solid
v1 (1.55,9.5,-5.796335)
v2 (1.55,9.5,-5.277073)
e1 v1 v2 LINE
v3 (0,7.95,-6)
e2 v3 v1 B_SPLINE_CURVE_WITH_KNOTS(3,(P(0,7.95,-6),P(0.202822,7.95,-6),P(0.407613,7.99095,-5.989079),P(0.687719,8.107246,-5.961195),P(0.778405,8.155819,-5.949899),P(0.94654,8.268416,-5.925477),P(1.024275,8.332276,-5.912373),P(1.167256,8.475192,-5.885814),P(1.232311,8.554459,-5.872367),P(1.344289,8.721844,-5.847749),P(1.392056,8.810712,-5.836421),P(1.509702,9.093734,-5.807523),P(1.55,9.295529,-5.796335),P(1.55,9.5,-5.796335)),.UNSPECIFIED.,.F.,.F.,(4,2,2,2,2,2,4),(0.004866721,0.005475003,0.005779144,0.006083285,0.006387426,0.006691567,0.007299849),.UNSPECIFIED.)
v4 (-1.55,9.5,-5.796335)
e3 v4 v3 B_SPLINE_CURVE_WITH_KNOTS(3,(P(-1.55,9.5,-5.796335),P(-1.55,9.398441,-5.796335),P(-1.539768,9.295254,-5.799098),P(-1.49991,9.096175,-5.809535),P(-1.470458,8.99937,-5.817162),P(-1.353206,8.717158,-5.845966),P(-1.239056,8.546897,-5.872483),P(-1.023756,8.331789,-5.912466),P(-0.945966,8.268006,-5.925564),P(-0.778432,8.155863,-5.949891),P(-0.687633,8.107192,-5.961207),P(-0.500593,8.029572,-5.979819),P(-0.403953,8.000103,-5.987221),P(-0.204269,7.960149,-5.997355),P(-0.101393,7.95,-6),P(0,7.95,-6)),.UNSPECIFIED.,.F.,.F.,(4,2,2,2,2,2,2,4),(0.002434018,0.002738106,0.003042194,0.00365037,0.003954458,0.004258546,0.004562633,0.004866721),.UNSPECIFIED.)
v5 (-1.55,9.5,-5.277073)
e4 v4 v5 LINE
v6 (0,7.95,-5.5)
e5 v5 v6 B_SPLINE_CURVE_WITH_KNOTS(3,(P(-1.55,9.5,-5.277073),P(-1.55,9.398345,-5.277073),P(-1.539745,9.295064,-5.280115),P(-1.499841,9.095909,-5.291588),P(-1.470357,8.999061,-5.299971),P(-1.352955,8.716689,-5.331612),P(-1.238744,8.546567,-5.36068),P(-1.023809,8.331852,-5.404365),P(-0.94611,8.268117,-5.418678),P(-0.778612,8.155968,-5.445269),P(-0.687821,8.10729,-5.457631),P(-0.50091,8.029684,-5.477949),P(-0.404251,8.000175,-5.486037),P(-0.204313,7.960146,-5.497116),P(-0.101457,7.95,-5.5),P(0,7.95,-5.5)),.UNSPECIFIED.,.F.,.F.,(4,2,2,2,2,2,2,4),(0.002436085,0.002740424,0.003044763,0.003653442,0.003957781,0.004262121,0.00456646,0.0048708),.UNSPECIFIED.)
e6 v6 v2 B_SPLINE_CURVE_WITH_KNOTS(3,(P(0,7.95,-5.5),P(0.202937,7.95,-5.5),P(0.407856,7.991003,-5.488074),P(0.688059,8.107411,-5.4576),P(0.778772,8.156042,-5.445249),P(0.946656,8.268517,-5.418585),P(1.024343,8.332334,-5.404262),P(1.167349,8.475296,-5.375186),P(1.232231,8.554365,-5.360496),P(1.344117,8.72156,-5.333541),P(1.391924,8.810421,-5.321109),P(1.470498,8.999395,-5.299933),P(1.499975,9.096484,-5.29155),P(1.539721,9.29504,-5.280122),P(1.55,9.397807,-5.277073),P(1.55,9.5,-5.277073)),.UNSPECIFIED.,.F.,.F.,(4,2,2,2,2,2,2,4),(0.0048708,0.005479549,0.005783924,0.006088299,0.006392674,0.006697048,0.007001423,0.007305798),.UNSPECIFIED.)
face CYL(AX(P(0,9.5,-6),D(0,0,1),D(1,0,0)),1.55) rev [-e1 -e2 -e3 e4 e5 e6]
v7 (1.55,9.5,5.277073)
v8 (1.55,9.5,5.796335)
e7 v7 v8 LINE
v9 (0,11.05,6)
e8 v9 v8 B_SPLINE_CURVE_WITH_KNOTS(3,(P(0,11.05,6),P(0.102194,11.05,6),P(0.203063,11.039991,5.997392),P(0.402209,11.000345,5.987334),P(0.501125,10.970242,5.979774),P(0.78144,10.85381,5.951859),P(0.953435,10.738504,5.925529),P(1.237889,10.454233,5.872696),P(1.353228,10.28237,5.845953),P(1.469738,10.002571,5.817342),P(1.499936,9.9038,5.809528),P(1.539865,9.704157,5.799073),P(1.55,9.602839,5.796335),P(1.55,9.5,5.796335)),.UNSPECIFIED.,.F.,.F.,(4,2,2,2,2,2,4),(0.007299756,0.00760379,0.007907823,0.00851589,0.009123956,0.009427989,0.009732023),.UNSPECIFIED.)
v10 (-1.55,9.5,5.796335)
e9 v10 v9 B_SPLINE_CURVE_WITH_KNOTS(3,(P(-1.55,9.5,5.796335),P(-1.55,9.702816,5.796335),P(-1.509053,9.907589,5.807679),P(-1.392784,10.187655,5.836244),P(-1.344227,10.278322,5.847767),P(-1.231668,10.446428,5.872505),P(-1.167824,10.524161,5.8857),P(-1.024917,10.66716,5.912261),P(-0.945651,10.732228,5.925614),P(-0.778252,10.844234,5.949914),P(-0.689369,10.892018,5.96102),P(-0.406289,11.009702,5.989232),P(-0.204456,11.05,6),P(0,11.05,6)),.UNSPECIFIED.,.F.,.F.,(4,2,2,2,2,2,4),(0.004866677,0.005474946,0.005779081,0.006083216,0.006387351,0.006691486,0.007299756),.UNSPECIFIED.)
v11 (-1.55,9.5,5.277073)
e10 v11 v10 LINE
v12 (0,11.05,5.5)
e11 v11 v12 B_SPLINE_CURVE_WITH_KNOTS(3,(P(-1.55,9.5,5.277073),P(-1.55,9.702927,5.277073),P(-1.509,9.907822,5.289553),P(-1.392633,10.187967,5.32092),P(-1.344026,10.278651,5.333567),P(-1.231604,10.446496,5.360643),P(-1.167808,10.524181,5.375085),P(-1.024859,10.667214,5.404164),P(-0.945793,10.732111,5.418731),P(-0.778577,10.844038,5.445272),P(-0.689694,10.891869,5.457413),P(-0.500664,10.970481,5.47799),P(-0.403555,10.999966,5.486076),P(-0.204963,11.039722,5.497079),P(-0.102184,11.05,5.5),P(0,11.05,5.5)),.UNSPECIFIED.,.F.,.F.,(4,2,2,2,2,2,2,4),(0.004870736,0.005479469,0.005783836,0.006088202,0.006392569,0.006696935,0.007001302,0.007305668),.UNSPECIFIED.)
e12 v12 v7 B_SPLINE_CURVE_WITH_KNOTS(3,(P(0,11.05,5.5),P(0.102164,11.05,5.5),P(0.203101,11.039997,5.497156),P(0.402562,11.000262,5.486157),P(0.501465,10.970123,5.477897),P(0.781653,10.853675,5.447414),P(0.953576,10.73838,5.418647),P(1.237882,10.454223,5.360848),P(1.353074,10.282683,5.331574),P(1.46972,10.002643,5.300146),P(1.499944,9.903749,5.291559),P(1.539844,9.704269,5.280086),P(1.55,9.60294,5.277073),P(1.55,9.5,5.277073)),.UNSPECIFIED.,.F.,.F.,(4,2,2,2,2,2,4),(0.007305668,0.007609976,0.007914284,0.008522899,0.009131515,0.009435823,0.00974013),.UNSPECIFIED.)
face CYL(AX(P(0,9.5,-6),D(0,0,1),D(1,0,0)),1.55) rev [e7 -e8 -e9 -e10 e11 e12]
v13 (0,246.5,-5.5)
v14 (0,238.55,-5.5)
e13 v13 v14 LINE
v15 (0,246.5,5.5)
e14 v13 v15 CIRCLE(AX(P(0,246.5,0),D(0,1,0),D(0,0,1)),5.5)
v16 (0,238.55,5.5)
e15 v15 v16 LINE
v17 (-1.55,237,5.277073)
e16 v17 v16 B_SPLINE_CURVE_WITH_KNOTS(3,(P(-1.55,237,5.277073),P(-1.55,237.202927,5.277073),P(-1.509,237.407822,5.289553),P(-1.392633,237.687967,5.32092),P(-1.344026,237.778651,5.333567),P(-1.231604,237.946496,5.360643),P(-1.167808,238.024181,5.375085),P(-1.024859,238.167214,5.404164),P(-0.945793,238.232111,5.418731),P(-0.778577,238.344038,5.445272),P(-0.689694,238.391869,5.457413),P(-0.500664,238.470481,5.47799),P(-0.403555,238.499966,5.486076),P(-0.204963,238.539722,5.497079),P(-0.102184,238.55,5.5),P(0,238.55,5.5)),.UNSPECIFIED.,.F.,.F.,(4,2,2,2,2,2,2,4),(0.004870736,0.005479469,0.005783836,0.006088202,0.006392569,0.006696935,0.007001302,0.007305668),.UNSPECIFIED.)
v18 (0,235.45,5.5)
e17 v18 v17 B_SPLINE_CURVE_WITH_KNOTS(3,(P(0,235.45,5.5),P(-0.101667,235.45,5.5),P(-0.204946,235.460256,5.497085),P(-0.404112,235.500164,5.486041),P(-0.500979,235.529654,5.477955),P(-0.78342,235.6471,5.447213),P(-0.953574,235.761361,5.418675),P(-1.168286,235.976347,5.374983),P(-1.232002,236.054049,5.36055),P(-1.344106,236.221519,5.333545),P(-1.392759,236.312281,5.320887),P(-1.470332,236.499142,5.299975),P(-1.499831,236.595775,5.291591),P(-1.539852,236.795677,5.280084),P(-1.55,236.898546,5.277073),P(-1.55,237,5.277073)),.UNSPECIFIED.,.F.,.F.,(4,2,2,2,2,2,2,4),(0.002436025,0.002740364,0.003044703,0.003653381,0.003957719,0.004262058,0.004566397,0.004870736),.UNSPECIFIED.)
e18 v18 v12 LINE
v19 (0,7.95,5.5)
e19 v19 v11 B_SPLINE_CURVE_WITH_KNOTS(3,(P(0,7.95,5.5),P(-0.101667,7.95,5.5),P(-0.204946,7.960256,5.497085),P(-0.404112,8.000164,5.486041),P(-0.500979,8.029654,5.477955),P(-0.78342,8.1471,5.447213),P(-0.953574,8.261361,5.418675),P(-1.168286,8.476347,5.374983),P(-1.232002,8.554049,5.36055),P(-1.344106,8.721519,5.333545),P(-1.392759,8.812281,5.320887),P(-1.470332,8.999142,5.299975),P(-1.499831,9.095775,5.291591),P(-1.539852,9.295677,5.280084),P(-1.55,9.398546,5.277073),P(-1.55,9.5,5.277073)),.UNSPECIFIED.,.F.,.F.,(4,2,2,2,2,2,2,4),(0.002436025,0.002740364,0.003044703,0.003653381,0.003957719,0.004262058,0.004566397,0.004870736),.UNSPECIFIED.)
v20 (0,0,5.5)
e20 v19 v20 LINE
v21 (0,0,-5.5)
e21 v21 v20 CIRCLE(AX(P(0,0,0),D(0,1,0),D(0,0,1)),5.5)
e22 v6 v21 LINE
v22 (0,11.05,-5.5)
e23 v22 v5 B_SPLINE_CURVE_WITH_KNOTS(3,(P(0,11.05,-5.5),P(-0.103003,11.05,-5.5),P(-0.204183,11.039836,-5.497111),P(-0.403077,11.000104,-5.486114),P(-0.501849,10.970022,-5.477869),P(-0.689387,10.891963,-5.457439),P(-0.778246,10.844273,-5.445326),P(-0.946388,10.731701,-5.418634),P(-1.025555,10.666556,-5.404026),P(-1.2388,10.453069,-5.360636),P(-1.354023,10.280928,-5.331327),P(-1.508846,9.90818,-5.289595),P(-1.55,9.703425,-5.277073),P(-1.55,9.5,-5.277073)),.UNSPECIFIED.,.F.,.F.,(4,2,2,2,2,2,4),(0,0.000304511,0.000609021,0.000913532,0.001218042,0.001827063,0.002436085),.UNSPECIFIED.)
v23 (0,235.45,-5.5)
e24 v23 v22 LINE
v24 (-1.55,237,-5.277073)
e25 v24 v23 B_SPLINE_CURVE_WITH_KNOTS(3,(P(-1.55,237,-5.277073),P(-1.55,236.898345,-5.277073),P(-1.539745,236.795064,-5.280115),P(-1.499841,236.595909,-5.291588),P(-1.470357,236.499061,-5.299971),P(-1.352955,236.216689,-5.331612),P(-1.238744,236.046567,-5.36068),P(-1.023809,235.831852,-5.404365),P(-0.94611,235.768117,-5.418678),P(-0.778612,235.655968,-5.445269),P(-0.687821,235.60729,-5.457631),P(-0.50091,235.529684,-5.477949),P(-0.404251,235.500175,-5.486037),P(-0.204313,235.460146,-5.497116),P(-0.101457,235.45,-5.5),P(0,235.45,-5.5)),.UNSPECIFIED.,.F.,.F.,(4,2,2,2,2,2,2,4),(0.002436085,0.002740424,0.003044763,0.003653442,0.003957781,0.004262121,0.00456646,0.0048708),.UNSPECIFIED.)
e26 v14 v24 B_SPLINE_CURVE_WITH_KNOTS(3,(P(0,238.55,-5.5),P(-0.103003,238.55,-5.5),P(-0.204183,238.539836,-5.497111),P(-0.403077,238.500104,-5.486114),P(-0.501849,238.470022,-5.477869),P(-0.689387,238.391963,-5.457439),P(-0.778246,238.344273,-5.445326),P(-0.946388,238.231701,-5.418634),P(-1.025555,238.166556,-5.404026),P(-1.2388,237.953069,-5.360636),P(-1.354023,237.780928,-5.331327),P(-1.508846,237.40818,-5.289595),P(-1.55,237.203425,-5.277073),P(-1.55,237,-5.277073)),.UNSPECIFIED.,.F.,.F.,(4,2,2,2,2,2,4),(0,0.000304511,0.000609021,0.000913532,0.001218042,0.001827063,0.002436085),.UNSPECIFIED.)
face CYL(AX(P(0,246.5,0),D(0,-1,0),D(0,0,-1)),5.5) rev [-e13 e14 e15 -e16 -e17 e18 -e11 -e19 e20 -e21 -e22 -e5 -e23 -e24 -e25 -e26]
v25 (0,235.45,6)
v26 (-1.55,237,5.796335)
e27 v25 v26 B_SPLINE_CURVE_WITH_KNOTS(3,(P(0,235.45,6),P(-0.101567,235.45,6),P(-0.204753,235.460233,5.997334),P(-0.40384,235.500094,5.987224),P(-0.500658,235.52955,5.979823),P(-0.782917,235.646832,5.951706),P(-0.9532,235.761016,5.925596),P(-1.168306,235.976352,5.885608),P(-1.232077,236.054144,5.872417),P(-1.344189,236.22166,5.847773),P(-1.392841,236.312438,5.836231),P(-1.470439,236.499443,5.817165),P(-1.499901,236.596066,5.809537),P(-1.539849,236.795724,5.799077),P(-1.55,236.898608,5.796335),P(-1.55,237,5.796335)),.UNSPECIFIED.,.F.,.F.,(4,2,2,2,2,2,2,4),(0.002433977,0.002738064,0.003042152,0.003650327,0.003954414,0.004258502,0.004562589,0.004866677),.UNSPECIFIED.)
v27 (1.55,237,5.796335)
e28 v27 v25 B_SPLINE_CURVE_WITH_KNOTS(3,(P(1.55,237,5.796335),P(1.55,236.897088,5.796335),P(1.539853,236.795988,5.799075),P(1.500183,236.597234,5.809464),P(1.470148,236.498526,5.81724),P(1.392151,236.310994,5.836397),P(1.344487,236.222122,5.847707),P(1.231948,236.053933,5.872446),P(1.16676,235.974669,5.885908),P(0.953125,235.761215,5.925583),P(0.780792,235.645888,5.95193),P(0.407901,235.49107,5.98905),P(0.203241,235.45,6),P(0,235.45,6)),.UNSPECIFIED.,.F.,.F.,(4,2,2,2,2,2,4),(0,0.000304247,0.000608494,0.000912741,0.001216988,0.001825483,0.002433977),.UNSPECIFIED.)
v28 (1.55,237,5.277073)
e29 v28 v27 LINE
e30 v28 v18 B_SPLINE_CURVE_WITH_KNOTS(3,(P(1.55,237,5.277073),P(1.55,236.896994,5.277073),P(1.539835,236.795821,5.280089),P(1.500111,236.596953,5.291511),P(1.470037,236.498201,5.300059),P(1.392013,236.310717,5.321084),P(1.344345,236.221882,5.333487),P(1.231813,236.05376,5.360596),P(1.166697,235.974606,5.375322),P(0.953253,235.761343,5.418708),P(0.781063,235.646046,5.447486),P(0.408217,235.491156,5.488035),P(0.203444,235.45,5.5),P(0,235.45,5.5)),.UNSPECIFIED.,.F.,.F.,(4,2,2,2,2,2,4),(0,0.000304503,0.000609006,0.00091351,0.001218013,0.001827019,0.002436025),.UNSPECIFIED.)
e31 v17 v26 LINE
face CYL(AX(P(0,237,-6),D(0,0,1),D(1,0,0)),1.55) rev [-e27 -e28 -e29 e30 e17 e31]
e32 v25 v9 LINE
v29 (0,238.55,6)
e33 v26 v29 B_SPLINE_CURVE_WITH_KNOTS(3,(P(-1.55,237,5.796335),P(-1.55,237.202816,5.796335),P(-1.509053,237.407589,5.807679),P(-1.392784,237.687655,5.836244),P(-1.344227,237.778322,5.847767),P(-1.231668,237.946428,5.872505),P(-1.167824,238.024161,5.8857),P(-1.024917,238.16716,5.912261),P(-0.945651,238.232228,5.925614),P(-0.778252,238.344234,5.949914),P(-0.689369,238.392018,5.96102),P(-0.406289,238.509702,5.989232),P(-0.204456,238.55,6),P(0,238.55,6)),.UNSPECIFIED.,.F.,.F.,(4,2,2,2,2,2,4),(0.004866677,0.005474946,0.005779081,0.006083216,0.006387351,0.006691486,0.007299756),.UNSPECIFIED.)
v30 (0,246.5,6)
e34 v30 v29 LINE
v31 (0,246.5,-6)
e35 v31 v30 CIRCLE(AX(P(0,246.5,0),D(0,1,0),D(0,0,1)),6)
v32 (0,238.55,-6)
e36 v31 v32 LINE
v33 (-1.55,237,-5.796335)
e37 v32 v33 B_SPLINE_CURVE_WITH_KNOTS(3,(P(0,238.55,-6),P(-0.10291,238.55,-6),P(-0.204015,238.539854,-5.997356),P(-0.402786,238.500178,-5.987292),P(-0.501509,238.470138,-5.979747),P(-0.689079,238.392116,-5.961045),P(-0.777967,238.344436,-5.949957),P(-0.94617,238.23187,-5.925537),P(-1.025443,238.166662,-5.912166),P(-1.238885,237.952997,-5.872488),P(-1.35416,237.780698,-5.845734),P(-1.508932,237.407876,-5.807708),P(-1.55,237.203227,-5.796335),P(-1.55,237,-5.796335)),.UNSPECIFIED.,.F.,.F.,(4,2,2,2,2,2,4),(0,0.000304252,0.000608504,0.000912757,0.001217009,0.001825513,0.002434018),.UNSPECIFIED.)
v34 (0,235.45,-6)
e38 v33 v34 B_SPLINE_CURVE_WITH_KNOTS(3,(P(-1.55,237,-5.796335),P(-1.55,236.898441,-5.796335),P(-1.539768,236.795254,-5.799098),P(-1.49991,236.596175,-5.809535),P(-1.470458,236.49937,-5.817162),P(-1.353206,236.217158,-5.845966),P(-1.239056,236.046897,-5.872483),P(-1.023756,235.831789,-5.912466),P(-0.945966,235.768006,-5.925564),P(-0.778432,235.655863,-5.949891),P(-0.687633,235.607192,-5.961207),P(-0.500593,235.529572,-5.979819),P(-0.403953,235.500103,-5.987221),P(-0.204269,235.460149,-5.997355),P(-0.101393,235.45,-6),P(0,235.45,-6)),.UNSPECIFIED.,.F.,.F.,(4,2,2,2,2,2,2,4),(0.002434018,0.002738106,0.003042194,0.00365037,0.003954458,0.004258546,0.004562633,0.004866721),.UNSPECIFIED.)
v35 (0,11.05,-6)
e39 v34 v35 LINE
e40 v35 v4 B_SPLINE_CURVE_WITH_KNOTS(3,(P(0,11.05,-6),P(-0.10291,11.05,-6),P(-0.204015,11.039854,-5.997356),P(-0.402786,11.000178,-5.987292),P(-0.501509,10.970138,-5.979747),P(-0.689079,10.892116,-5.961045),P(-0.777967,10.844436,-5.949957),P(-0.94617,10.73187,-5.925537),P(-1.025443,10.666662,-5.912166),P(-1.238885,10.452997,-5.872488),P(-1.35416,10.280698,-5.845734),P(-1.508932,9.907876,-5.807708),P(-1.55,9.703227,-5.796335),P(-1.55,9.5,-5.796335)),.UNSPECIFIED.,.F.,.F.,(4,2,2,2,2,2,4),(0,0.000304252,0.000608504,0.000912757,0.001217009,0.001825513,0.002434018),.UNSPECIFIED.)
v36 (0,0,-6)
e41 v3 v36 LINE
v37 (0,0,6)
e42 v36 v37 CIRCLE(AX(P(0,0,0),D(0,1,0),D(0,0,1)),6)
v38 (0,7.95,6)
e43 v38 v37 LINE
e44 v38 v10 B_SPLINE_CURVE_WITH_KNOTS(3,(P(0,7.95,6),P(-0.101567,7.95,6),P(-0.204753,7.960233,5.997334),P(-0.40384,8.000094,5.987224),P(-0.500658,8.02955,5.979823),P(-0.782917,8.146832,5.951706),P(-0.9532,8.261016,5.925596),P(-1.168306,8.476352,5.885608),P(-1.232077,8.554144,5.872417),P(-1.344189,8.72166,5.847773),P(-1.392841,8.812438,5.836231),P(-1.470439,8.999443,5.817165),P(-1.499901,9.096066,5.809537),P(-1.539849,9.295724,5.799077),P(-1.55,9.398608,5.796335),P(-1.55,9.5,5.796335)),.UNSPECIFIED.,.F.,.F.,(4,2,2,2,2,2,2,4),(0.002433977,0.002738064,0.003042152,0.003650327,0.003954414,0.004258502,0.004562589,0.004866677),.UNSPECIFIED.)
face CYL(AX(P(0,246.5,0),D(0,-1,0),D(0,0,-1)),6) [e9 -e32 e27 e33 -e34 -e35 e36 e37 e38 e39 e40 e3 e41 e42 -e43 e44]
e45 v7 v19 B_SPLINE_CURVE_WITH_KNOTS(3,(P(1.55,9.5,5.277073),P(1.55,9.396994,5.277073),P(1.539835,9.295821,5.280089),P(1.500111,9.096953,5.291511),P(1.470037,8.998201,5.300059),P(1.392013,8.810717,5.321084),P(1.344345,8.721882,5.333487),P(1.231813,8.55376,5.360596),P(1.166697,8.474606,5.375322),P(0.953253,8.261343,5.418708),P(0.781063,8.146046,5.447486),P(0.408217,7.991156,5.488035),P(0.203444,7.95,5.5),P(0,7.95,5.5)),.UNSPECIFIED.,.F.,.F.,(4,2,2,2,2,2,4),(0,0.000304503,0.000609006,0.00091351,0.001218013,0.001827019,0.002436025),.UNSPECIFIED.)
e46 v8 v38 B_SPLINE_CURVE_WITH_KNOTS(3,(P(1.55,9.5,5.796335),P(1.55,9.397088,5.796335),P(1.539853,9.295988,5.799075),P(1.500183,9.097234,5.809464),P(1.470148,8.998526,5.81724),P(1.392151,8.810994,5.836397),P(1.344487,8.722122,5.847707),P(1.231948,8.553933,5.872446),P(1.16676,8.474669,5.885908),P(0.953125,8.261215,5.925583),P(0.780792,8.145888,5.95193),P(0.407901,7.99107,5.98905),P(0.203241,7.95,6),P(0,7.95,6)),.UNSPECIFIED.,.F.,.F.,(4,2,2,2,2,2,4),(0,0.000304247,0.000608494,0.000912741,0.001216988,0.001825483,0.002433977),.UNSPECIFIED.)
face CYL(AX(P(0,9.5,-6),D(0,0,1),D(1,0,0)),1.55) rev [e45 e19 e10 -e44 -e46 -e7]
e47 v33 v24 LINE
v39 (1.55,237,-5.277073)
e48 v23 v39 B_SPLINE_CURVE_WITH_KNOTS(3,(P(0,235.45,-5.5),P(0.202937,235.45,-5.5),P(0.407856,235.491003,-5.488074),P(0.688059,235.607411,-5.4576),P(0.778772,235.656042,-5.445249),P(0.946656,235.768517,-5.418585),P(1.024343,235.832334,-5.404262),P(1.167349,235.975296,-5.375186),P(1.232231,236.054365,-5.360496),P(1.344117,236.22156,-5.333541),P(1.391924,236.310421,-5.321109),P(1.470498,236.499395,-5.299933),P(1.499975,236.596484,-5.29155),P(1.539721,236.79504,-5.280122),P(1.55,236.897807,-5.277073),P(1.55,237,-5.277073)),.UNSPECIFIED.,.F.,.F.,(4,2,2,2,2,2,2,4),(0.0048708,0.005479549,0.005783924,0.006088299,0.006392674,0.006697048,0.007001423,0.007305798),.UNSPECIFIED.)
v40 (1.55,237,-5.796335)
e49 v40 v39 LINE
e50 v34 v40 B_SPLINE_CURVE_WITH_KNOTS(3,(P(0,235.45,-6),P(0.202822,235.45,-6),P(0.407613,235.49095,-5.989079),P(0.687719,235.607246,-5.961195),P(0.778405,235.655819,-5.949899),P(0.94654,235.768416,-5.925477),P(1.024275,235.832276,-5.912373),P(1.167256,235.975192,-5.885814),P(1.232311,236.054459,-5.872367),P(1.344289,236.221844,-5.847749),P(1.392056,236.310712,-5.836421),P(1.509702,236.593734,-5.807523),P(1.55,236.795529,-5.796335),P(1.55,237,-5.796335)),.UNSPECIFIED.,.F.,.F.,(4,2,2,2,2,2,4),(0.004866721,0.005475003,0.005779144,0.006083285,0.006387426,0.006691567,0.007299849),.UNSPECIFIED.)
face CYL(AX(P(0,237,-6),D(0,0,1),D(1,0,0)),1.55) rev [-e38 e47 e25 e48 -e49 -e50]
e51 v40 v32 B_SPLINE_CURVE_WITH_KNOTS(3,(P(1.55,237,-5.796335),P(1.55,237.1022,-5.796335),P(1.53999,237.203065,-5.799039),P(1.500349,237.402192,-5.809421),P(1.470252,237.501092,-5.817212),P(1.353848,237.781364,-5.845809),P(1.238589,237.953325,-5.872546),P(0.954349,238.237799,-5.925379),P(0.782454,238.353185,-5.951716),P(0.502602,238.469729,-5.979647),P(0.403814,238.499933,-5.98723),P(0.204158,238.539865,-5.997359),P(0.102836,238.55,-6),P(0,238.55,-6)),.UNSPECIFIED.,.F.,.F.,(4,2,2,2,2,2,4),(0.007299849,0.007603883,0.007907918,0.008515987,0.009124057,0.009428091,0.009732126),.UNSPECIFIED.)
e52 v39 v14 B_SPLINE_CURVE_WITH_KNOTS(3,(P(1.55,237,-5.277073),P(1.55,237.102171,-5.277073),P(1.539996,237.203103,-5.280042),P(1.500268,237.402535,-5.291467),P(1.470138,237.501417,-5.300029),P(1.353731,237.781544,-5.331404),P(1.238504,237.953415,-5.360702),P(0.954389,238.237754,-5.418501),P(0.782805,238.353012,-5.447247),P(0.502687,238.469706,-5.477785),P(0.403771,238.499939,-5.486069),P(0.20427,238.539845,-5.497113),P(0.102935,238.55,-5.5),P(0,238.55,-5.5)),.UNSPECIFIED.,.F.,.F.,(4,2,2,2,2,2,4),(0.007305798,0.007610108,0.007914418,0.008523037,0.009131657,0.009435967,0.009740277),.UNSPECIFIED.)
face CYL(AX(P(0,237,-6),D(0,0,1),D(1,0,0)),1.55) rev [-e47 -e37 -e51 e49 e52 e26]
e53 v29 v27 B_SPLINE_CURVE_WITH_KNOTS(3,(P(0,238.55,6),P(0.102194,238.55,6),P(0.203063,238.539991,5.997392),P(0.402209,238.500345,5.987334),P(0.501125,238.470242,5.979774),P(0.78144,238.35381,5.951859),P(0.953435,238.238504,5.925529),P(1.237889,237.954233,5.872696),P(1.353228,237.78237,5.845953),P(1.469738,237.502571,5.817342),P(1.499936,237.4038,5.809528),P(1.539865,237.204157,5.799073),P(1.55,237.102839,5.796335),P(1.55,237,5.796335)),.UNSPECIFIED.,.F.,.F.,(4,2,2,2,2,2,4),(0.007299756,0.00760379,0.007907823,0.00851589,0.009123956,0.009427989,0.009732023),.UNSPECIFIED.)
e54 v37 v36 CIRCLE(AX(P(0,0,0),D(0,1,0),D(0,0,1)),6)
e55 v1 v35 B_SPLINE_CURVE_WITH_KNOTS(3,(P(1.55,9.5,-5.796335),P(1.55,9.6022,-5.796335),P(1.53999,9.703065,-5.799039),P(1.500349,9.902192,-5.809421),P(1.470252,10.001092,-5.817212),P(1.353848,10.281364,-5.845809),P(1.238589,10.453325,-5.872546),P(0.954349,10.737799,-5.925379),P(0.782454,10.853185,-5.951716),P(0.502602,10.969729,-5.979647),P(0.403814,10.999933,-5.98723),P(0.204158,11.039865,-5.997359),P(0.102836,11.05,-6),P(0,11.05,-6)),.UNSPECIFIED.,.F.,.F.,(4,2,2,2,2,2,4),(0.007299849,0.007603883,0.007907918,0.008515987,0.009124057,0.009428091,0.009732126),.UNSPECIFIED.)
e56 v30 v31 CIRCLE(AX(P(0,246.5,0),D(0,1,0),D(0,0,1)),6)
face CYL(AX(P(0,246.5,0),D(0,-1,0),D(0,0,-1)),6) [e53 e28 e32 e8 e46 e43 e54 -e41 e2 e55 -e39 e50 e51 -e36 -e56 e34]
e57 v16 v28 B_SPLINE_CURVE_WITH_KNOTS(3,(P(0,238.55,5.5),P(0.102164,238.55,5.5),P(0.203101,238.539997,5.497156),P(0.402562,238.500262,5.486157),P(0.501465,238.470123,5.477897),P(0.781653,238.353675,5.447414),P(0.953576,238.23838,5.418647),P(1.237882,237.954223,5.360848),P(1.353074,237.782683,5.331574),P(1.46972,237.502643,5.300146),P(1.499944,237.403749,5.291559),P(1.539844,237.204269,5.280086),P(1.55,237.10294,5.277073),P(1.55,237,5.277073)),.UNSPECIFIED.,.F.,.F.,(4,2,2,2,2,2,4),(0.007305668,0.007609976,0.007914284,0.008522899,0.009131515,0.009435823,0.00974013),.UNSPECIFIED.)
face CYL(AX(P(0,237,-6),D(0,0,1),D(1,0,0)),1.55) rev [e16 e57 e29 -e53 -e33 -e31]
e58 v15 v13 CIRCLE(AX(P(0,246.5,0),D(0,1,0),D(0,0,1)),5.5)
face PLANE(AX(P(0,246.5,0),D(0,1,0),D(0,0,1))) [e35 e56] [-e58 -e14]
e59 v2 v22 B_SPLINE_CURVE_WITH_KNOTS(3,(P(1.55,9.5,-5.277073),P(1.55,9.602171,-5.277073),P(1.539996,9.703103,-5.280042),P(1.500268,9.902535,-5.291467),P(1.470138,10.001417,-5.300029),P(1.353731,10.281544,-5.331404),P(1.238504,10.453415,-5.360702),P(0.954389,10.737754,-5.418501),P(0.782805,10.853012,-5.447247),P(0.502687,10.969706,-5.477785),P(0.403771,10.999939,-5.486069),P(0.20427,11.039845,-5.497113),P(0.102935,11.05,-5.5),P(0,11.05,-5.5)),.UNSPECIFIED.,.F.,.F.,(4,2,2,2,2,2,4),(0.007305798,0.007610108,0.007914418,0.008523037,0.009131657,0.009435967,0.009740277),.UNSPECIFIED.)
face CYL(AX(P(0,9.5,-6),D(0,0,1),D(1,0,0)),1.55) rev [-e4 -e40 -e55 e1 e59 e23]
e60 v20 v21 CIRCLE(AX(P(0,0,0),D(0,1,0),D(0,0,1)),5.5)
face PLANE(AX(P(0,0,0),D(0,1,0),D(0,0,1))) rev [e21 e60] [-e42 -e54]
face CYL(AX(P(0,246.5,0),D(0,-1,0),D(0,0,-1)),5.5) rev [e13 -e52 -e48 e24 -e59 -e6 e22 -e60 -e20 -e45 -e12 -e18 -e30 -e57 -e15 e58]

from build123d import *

# Parameters (mm, degrees)
SKETCH_1_R               = 6
SKETCH_1_R_2             = 5.5
EXTRUDE_1_DEPTH          = 246.5
CUT_EXTRUDE_1_DEPTH      = 247.646001387
CUT_EXTRUDE_1_DEPTH_BACK = 247.646001387
SKETCH_2_R               = 1.55


with BuildPart() as part:
    # 草图1 → 凸台-拉伸1 (new body)
    with BuildSketch(Plane(origin=(0, 0, 0), x_dir=(1, 0, 0), z_dir=(0, 1, 0))):
        with Locations(Location((0, 0, 0), (0, 0, 270))):
            Circle(SKETCH_1_R)
        with Locations(Location((0, 0, 0), (0, 0, 270))):
            Circle(SKETCH_1_R_2, mode=Mode.SUBTRACT)
    extrude(amount=EXTRUDE_1_DEPTH)

    # 草图2 → 切除-拉伸1 (cut, two sides: drawn at the far end of the back side and taken through both)
    with BuildSketch(Plane.XY.offset(-CUT_EXTRUDE_1_DEPTH_BACK)):
        with Locations((0, 237)):
            Circle(SKETCH_2_R)
        with Locations((0, 9.5)):
            Circle(SKETCH_2_R)
    extrude(amount=CUT_EXTRUDE_1_DEPTH + CUT_EXTRUDE_1_DEPTH_BACK, mode=Mode.SUBTRACT)


solid = part.part
